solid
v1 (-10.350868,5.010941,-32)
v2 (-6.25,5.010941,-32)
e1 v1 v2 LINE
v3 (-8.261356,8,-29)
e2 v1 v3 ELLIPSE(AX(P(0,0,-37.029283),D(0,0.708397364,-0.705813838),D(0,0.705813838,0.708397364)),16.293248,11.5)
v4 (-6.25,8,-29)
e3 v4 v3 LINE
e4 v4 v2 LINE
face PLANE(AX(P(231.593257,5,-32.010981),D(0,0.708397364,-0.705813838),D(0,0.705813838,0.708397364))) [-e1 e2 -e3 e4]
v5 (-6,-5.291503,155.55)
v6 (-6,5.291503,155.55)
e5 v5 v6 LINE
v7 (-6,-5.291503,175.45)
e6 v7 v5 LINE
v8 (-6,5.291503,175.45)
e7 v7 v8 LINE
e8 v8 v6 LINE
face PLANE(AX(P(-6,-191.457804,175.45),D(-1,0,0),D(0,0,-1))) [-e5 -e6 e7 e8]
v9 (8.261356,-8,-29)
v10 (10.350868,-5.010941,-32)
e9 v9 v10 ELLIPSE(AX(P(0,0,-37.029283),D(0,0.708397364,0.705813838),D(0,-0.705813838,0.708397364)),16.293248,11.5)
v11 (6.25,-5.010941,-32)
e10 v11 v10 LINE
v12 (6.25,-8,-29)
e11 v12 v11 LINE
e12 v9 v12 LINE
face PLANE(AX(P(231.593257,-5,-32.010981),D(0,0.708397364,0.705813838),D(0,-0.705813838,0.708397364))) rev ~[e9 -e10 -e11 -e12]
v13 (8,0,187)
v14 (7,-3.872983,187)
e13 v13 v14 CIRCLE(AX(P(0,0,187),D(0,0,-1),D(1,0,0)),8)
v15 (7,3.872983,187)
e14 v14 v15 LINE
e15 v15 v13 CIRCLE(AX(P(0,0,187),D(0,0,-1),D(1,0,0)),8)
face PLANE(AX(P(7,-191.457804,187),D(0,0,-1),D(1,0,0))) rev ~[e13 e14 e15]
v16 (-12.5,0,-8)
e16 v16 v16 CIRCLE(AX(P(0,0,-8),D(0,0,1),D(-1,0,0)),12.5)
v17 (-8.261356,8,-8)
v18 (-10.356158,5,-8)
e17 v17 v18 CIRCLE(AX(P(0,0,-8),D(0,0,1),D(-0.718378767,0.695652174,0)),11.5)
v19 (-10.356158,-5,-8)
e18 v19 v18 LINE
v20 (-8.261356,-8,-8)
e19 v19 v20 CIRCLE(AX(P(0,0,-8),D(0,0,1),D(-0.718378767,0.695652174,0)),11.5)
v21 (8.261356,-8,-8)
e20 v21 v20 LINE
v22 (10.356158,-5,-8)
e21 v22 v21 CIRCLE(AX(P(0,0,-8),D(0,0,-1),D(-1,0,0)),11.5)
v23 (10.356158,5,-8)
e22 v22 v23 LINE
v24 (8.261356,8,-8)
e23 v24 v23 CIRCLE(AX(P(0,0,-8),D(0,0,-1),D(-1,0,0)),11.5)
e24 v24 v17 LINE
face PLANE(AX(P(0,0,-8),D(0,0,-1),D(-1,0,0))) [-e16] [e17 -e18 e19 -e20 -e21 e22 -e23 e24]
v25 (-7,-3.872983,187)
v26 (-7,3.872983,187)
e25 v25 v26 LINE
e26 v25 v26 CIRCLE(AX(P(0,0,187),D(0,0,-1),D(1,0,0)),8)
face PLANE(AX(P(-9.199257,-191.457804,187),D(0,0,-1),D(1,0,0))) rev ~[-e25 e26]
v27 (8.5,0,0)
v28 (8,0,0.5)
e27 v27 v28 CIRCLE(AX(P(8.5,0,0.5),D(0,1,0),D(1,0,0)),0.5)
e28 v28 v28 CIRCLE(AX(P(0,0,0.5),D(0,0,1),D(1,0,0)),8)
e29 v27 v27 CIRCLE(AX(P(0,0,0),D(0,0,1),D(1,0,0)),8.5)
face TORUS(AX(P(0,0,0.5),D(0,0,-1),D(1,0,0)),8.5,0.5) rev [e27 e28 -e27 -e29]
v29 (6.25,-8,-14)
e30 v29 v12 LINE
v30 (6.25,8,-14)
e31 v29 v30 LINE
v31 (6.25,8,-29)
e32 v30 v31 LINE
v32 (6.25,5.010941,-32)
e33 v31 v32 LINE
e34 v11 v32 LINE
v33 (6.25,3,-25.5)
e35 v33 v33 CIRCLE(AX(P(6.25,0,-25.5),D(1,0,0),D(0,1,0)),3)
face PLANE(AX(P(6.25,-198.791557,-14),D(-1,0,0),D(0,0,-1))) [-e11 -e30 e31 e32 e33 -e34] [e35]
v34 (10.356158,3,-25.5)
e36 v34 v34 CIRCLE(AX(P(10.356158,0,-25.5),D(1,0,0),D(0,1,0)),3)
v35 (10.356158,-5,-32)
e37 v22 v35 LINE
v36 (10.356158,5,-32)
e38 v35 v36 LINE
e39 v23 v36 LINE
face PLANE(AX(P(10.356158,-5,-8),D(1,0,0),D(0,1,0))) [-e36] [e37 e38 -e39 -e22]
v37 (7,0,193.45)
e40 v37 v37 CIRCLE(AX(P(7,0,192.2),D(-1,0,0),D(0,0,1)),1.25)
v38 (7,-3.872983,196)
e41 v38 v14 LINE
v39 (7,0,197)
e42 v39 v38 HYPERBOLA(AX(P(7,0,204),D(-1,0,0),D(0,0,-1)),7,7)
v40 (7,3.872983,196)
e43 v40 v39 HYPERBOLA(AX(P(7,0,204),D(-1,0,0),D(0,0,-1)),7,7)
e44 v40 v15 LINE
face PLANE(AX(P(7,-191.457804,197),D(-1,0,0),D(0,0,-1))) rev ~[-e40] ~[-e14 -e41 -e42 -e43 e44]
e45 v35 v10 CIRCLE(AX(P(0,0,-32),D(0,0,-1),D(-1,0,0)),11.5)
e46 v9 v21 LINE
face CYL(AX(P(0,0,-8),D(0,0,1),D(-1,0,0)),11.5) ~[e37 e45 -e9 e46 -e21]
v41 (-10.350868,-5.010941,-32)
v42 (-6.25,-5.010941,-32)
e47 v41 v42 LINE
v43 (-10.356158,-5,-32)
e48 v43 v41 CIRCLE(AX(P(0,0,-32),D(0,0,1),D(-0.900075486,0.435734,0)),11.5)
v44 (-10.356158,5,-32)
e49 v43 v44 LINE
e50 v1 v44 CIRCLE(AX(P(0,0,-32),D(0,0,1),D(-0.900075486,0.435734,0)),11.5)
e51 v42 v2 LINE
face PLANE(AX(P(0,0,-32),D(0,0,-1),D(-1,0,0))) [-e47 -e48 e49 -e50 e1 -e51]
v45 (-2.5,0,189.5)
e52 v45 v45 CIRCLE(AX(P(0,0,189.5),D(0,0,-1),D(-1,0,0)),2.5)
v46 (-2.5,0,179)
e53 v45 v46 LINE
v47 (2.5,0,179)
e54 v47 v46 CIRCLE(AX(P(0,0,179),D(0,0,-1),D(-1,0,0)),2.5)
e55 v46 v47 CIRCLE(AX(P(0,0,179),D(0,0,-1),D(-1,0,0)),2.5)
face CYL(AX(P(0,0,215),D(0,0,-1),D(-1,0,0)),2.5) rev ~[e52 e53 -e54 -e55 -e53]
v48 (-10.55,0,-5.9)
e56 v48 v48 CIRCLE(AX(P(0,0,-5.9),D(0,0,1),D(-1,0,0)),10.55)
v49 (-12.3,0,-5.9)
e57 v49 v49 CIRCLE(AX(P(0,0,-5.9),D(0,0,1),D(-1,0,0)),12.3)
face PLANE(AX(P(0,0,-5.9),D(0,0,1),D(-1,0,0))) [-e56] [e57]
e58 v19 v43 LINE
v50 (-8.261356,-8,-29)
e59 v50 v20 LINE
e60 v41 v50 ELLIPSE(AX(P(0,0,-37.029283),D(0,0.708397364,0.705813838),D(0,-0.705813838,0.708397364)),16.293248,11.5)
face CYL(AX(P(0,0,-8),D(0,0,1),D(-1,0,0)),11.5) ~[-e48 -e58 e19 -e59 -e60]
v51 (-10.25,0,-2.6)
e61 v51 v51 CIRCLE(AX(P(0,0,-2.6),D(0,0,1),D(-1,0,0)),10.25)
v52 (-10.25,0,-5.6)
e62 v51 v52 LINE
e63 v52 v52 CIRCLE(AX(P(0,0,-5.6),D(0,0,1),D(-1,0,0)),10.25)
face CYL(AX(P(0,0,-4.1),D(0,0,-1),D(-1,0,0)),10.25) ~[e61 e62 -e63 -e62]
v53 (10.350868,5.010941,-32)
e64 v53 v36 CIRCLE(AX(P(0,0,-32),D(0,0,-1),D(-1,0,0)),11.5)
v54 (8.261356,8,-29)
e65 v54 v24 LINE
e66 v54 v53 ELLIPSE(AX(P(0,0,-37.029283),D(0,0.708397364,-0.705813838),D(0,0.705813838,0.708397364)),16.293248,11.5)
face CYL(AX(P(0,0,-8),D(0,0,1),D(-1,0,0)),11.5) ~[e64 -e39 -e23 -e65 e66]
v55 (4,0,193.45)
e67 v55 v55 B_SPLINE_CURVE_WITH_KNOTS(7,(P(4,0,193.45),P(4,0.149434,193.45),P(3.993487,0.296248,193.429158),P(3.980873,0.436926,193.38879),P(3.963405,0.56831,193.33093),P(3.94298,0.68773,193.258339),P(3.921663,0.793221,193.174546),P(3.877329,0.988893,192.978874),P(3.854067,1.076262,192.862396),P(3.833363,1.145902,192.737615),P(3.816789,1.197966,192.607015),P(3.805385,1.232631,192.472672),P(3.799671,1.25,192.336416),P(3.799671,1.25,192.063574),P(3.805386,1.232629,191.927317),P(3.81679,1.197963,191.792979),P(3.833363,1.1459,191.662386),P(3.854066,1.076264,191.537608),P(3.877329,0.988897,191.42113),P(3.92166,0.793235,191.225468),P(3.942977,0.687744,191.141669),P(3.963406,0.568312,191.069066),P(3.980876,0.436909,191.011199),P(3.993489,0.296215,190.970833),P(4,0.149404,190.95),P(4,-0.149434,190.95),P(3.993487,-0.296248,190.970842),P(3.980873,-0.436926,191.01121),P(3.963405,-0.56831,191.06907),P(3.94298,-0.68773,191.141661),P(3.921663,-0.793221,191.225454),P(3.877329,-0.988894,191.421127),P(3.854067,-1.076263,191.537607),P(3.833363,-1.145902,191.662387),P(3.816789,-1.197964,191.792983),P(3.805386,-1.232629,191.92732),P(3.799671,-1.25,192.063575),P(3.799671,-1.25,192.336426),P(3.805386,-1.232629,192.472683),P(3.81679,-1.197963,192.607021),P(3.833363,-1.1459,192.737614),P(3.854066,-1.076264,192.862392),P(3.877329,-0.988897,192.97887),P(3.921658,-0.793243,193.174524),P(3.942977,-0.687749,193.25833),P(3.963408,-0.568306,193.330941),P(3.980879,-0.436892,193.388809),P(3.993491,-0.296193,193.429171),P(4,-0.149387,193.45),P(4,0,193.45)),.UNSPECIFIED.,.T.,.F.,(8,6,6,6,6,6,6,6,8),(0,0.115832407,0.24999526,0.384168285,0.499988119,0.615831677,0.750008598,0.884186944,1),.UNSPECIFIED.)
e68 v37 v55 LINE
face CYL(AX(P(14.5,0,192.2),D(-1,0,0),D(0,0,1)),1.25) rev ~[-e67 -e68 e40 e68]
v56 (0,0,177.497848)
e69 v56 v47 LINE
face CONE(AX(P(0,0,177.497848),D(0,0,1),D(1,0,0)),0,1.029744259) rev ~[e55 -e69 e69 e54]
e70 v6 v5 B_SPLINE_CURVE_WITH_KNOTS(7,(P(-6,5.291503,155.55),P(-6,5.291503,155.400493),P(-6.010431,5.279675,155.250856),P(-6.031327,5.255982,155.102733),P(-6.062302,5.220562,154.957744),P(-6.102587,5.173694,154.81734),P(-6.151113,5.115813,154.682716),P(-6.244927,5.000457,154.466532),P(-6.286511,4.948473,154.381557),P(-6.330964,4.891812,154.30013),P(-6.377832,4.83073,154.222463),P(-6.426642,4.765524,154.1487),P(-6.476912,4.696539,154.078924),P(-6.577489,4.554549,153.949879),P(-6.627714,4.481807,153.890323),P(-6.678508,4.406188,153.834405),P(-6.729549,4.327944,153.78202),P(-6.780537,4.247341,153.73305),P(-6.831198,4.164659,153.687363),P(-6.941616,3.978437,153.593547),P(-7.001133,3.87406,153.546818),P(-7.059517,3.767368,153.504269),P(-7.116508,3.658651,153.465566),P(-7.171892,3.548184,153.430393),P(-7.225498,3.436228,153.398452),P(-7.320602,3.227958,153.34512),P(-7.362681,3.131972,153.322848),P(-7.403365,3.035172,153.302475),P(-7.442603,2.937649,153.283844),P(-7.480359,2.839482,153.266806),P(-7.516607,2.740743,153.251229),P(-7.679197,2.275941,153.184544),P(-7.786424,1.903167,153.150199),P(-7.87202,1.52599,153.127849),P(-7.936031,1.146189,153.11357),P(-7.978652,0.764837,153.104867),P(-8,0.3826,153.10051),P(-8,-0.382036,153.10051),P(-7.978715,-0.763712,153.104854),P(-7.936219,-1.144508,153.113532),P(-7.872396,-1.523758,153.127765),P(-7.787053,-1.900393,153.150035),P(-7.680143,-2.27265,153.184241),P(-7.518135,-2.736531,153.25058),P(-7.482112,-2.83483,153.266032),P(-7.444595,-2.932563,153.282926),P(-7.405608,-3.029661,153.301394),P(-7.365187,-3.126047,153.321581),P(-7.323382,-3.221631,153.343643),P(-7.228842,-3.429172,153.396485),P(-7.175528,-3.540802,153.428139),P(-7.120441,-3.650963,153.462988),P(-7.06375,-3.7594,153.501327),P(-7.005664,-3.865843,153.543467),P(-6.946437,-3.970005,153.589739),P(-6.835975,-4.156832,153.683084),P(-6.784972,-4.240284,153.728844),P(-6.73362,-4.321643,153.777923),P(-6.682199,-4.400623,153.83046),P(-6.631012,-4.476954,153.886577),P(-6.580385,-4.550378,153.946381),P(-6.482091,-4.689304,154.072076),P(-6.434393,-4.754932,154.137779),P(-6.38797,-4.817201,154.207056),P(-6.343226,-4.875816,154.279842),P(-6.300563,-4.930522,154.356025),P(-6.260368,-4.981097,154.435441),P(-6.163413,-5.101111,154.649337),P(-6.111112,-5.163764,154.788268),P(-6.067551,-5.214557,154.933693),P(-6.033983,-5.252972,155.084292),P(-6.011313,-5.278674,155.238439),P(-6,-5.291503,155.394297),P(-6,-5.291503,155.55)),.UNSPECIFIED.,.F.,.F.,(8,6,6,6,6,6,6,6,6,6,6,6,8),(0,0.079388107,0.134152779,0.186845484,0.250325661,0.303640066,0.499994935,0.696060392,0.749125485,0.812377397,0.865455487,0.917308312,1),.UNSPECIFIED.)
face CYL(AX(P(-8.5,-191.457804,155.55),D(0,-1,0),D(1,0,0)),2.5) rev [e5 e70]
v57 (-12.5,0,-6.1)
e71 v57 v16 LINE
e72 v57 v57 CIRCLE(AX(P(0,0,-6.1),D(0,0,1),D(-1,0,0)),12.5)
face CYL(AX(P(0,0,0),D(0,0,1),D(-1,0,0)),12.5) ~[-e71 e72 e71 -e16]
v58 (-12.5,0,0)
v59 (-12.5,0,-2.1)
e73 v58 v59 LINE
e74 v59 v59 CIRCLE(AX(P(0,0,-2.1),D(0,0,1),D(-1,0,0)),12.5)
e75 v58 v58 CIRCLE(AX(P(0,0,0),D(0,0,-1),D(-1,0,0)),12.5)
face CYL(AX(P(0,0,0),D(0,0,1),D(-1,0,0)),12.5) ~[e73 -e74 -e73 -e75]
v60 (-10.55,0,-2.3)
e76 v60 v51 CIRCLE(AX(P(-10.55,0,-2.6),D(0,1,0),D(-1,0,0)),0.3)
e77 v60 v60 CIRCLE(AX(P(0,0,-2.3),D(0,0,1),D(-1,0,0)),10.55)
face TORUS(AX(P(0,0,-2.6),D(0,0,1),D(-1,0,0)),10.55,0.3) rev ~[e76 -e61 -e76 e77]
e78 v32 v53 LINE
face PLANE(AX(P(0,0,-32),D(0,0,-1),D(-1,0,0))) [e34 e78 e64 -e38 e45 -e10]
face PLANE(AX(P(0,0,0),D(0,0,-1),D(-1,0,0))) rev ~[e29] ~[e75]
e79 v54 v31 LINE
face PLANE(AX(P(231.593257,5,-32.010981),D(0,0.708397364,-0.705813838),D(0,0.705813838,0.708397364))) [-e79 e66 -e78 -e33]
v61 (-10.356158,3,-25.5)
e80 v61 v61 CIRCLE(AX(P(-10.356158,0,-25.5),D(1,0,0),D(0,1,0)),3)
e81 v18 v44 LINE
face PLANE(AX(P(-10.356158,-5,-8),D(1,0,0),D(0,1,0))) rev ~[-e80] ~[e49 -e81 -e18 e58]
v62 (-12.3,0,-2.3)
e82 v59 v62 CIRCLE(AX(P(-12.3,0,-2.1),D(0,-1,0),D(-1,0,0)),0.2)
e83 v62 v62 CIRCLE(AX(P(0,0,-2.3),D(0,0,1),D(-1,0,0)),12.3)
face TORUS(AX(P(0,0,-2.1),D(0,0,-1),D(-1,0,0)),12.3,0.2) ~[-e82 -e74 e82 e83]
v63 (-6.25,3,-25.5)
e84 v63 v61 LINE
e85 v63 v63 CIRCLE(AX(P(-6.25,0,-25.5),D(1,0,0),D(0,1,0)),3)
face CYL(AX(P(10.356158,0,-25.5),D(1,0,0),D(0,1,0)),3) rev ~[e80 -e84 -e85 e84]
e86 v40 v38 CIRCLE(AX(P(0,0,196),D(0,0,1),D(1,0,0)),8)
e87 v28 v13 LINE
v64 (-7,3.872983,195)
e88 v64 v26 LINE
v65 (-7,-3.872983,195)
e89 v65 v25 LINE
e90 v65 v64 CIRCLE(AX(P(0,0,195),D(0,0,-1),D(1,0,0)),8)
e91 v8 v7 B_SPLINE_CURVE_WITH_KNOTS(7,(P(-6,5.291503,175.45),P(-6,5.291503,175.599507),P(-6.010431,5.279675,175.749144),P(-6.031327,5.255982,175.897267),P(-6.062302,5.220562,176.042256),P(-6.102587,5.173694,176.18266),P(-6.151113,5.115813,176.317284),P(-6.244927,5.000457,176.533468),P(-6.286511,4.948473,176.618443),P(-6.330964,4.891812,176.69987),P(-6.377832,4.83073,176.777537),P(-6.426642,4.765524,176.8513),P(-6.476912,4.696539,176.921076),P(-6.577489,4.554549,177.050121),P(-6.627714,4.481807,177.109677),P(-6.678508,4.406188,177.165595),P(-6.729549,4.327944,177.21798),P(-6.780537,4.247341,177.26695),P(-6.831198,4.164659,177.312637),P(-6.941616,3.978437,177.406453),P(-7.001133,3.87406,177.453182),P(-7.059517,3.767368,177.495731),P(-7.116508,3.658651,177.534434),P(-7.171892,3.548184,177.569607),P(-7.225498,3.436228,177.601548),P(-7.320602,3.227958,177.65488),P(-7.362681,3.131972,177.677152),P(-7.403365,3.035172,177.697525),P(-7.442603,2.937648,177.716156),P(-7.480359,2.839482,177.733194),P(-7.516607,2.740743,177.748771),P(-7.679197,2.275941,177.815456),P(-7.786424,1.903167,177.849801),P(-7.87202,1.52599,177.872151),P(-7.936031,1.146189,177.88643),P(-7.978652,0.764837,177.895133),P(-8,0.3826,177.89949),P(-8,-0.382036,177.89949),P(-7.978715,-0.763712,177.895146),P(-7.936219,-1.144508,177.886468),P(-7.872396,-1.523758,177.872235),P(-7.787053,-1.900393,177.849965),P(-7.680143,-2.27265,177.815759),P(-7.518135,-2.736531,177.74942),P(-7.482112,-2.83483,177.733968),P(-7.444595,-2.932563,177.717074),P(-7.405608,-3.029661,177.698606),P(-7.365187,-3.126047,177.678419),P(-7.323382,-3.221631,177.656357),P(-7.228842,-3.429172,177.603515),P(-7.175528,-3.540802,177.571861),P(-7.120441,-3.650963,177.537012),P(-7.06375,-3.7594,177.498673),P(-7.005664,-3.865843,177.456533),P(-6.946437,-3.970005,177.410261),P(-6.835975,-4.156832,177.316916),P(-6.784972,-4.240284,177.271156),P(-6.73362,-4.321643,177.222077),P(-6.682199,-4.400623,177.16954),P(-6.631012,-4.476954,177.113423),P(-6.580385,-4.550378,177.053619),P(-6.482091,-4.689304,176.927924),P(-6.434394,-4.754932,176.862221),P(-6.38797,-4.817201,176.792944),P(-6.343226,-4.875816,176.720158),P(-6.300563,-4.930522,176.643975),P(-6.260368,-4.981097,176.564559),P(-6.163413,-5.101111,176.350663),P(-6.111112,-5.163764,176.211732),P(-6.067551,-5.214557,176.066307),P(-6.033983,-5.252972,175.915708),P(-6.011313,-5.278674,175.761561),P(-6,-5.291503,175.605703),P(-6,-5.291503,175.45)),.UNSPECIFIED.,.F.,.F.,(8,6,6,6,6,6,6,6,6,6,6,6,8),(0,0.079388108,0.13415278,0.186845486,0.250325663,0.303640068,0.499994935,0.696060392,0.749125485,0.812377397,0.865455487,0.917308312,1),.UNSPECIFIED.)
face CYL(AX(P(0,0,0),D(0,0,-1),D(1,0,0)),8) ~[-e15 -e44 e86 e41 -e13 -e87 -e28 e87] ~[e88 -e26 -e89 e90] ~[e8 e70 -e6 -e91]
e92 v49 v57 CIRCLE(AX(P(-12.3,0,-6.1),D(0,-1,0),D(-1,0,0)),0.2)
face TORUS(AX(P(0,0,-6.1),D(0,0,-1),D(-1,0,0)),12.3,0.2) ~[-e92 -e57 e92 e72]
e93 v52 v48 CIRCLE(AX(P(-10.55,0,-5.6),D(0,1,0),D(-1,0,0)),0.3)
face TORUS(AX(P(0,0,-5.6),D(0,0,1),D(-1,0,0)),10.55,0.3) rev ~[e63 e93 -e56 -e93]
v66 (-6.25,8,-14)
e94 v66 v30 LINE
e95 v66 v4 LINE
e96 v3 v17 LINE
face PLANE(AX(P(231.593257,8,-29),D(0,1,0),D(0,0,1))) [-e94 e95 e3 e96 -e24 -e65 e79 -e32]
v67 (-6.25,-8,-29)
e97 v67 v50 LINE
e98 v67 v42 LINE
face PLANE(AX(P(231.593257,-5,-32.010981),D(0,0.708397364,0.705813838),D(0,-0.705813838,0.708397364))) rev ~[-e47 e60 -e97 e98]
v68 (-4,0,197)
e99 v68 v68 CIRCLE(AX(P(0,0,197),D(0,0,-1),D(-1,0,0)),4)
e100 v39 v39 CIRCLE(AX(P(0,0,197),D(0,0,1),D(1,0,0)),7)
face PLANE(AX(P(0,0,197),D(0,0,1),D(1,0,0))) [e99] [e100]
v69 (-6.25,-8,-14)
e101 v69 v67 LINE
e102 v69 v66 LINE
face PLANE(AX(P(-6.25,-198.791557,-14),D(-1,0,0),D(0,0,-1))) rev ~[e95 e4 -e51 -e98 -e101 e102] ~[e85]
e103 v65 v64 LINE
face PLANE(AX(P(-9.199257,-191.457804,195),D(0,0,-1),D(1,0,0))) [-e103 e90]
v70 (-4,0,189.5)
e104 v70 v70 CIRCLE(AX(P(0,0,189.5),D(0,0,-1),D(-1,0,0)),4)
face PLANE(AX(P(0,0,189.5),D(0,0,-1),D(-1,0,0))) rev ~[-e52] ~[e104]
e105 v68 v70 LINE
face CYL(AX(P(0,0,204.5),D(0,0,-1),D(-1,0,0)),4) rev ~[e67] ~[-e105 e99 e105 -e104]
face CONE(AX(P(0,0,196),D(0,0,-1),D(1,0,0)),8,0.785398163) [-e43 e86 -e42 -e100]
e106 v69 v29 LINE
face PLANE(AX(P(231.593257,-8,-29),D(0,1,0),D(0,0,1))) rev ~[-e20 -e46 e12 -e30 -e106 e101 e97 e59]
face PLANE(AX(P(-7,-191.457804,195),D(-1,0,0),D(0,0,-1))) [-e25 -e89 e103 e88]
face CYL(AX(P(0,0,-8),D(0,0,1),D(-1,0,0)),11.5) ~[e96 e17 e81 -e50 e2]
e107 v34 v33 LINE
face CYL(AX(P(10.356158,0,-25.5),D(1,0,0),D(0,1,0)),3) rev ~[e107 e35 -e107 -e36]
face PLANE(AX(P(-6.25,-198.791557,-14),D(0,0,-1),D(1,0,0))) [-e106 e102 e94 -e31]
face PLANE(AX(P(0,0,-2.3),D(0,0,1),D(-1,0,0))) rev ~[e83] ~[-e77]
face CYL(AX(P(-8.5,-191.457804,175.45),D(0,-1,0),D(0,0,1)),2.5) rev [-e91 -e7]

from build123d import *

# Parameters (mm, degrees)
SKETCH1_R               = 8
BOSS_EXTRUDE1_DEPTH     = 197
SKETCH2_R               = 12.5
BOSS_EXTRUDE2_DEPTH     = 8
SKETCH3_W               = 2.25
SKETCH3_H               = 3.6
SKETCH8_R               = 11.5
BOSS_EXTRUDE4_DEPTH     = 24
CUT_EXTRUDE1_DEPTH      = 198.791556948
CUT_EXTRUDE1_DEPTH_BACK = 198.791556948
SKETCH10_W              = 12.5
SKETCH10_H              = 21.605782088
CUT_EXTRUDE3_DEPTH      = 231.593256623
CUT_EXTRUDE3_DEPTH_BACK = 231.593256623
CUT_EXTRUDE5_START      = -24
CUT_EXTRUDE5_DEPTH      = 24
FILLET1_R               = 0.5
FILLET2_R               = 0.2
FILLET3_R               = 0.3
CHAMFER3_SIZE           = 1
CUT_EXTRUDE7_DEPTH      = 199.457804086
CUT_EXTRUDE7_DEPTH_BACK = 199.457804086
SKETCH15_W              = 2.199256875
SKETCH15_H              = 8
SKETCH15_W_2            = 2.880068719
SKETCH15_H_2            = 10
SKETCH14_R              = 3
CUT_EXTRUDE6_DEPTH      = 24
HOLE2_D                 = 8
HOLE2_DEPTH             = 7.5
M6_TAPPED_HOLE1_D       = 5
M6_TAPPED_HOLE1_DEPTH   = 18
M6_TAPPED_HOLE1_TIP     = 1.502151548
M3_TAPPED_HOLE1_D       = 2.5
M3_TAPPED_HOLE1_DEPTH   = 7.5
M3_TAPPED_HOLE1_TIP     = 0.751075774


with BuildPart() as part:
    # Sketch1 → Boss-Extrude1 (new body)
    with BuildSketch(Plane.XY):
        Circle(SKETCH1_R)
    extrude(amount=BOSS_EXTRUDE1_DEPTH)

    # Sketch2 → Boss-Extrude2 (add)
    with BuildSketch(Plane(origin=(0, 0, 0), x_dir=(-1, 0, 0), z_dir=(0, 0, -1))):
        Circle(SKETCH2_R)
    extrude(amount=BOSS_EXTRUDE2_DEPTH)

    # Sketch3 → Cut-Revolve1 (revolve, cut)
    with BuildSketch(Plane(origin=(0, 0, 0), x_dir=(1, 0, 0), z_dir=(0, 1, 0))):
        with Locations((-11.375, 4.1)):
            Rectangle(SKETCH3_W, SKETCH3_H)
    revolve(axis=Axis((0, 0, -10.00817261), (0, 0, 1)), mode=Mode.SUBTRACT)

    # Sketch8 → Boss-Extrude4 (add)
    with BuildSketch(Plane(origin=(0, 0, -8), x_dir=(-1, 0, 0), z_dir=(0, 0, -1))):
        Circle(SKETCH8_R)
    extrude(amount=BOSS_EXTRUDE4_DEPTH)

    # Sketch10 → Cut-Extrude1 (cut, two sides: drawn at the far end of the back side and taken through both)
    with BuildSketch(Plane(origin=(0, 0, 0), x_dir=(1, 0, 0), z_dir=(0, 1, 0)).offset(-CUT_EXTRUDE1_DEPTH_BACK)):
        with Locations((0, 24.802891044)):
            Rectangle(SKETCH10_W, SKETCH10_H)
    extrude(amount=CUT_EXTRUDE1_DEPTH + CUT_EXTRUDE1_DEPTH_BACK, mode=Mode.SUBTRACT)

    # Sketch11 → Cut-Extrude3 (cut, two sides: drawn at the far end of the back side and taken through both)
    with BuildSketch(Plane(origin=(0, -11.5, -32), x_dir=(0, 0, -1), z_dir=(-1, 0, 0)).offset(-CUT_EXTRUDE3_DEPTH_BACK)):
        Polygon((0.010981051, -16.5), (-3, -19.5), (-24, -19.5), (-24, -26.396557876), (1.498378991, -26.396557876), (1.498378991, -19.5), (0.010981051, -19.5), align=None)
        Polygon((-24, -3.5), (-24, 3.359688932), (2.769529036, 3.359688932), (2.769529036, -3.5), (1.498378991, -3.5), (0.010981051, -3.5), (0.010981051, -6.5), (-3, -3.5), align=None)
    extrude(amount=CUT_EXTRUDE3_DEPTH + CUT_EXTRUDE3_DEPTH_BACK, mode=Mode.SUBTRACT)

    # Sketch13 → Cut-Extrude5 (cut)
    with BuildSketch(Plane(origin=(0, 0, -32), x_dir=(-1, 0, 0), z_dir=(0, 0, -1)).offset(CUT_EXTRUDE5_START)):
        with BuildLine():
            Line((10.356157589, -5), (10.356157589, 5))
            ThreePointArc((10.356157589, 5), (11.5, 0), (10.356157589, -5))
        make_face()
        with BuildLine():
            Line((-10.356157589, -5), (-10.356157589, 5))
            ThreePointArc((-10.356157589, 5), (-11.5, 0), (-10.356157589, -5))
        make_face()
    extrude(amount=CUT_EXTRUDE5_DEPTH, mode=Mode.SUBTRACT)

    # Fillet1
    fillet1_edges = [part.edges().sort_by_distance(p)[0] for p in [
        (-8, 0, 0),
    ]]
    fillet(fillet1_edges, radius=FILLET1_R)

    # Fillet2
    fillet2_edges = [part.edges().sort_by_distance(p)[0] for p in [
        (12.5, 0, -2.3),
        (12.5, 0, -5.9),
    ]]
    fillet(fillet2_edges, radius=FILLET2_R)

    # Fillet3
    fillet3_edges = [part.edges().sort_by_distance(p)[0] for p in [
        (10.25, 0, -2.3),
        (10.25, 0, -5.9),
    ]]
    fillet(fillet3_edges, radius=FILLET3_R)

    # Chamfer3
    chamfer3_edges = [part.edges().sort_by_distance(p)[0] for p in [
        (-8, 0, 197),
    ]]
    chamfer(chamfer3_edges, length=CHAMFER3_SIZE)

    # Sketch15 → Cut-Extrude7 (cut, two sides: drawn at the far end of the back side and taken through both)
    with BuildSketch(Plane(origin=(0, 8, 0), x_dir=(1, 0, 0), z_dir=(0, 1, 0)).offset(-CUT_EXTRUDE7_DEPTH_BACK)):
        with Locations((-8.099628438, -191)):
            Rectangle(SKETCH15_W, SKETCH15_H)
        with BuildLine():
            Line((-8.5, -153.05), (-9.470215056, -153.05))
            Line((-9.470215056, -153.05), (-9.470215056, -177.95))
            Line((-9.470215056, -177.95), (-8.5, -177.95))
            ThreePointArc((-8.5, -177.95), (-6.732233047, -177.217766953), (-6, -175.45))
            Line((-6, -175.45), (-6, -155.55))
            ThreePointArc((-6, -155.55), (-6.732233047, -153.782233047), (-8.5, -153.05))
        make_face()
        with Locations((8.44003436, -192)):
            Rectangle(SKETCH15_W_2, SKETCH15_H_2)
    extrude(amount=CUT_EXTRUDE7_DEPTH + CUT_EXTRUDE7_DEPTH_BACK, mode=Mode.SUBTRACT)

    # Sketch14 → Cut-Extrude6 (cut)
    with BuildSketch(Plane(origin=(10.356157589, 0, 0), x_dir=(0, 0, -1), z_dir=(1, 0, 0))):
        with Locations(Location((25.5, 0, 0), (0, 0, 90))):
            Circle(SKETCH14_R)
    extrude(amount=-CUT_EXTRUDE6_DEPTH, mode=Mode.SUBTRACT)

    # Hole2
    with Locations(Plane.XY.offset(197)):
        with Locations((0, 0)):
            Hole(HOLE2_D / 2, depth=HOLE2_DEPTH)

    # M6 Tapped Hole1
    with Locations(Plane.XY.offset(197)):
        with Locations((0, 0)):
            Hole(M6_TAPPED_HOLE1_D / 2, depth=M6_TAPPED_HOLE1_DEPTH)
            with Locations((0, 0, -(M6_TAPPED_HOLE1_DEPTH + M6_TAPPED_HOLE1_TIP / 2))):  # 118° drill point
                Cone(0, M6_TAPPED_HOLE1_D / 2, M6_TAPPED_HOLE1_TIP, mode=Mode.SUBTRACT)

    # M3 Tapped Hole1
    with Locations(Plane(origin=(7, 0, 0), x_dir=(0, 0, -1), z_dir=(1, 0, 0))):
        with Locations((-192.2, 0)):
            Hole(M3_TAPPED_HOLE1_D / 2, depth=M3_TAPPED_HOLE1_DEPTH)
            with Locations((0, 0, -(M3_TAPPED_HOLE1_DEPTH + M3_TAPPED_HOLE1_TIP / 2))):  # 118° drill point
                Cone(0, M3_TAPPED_HOLE1_D / 2, M3_TAPPED_HOLE1_TIP, mode=Mode.SUBTRACT)


solid = part.part
